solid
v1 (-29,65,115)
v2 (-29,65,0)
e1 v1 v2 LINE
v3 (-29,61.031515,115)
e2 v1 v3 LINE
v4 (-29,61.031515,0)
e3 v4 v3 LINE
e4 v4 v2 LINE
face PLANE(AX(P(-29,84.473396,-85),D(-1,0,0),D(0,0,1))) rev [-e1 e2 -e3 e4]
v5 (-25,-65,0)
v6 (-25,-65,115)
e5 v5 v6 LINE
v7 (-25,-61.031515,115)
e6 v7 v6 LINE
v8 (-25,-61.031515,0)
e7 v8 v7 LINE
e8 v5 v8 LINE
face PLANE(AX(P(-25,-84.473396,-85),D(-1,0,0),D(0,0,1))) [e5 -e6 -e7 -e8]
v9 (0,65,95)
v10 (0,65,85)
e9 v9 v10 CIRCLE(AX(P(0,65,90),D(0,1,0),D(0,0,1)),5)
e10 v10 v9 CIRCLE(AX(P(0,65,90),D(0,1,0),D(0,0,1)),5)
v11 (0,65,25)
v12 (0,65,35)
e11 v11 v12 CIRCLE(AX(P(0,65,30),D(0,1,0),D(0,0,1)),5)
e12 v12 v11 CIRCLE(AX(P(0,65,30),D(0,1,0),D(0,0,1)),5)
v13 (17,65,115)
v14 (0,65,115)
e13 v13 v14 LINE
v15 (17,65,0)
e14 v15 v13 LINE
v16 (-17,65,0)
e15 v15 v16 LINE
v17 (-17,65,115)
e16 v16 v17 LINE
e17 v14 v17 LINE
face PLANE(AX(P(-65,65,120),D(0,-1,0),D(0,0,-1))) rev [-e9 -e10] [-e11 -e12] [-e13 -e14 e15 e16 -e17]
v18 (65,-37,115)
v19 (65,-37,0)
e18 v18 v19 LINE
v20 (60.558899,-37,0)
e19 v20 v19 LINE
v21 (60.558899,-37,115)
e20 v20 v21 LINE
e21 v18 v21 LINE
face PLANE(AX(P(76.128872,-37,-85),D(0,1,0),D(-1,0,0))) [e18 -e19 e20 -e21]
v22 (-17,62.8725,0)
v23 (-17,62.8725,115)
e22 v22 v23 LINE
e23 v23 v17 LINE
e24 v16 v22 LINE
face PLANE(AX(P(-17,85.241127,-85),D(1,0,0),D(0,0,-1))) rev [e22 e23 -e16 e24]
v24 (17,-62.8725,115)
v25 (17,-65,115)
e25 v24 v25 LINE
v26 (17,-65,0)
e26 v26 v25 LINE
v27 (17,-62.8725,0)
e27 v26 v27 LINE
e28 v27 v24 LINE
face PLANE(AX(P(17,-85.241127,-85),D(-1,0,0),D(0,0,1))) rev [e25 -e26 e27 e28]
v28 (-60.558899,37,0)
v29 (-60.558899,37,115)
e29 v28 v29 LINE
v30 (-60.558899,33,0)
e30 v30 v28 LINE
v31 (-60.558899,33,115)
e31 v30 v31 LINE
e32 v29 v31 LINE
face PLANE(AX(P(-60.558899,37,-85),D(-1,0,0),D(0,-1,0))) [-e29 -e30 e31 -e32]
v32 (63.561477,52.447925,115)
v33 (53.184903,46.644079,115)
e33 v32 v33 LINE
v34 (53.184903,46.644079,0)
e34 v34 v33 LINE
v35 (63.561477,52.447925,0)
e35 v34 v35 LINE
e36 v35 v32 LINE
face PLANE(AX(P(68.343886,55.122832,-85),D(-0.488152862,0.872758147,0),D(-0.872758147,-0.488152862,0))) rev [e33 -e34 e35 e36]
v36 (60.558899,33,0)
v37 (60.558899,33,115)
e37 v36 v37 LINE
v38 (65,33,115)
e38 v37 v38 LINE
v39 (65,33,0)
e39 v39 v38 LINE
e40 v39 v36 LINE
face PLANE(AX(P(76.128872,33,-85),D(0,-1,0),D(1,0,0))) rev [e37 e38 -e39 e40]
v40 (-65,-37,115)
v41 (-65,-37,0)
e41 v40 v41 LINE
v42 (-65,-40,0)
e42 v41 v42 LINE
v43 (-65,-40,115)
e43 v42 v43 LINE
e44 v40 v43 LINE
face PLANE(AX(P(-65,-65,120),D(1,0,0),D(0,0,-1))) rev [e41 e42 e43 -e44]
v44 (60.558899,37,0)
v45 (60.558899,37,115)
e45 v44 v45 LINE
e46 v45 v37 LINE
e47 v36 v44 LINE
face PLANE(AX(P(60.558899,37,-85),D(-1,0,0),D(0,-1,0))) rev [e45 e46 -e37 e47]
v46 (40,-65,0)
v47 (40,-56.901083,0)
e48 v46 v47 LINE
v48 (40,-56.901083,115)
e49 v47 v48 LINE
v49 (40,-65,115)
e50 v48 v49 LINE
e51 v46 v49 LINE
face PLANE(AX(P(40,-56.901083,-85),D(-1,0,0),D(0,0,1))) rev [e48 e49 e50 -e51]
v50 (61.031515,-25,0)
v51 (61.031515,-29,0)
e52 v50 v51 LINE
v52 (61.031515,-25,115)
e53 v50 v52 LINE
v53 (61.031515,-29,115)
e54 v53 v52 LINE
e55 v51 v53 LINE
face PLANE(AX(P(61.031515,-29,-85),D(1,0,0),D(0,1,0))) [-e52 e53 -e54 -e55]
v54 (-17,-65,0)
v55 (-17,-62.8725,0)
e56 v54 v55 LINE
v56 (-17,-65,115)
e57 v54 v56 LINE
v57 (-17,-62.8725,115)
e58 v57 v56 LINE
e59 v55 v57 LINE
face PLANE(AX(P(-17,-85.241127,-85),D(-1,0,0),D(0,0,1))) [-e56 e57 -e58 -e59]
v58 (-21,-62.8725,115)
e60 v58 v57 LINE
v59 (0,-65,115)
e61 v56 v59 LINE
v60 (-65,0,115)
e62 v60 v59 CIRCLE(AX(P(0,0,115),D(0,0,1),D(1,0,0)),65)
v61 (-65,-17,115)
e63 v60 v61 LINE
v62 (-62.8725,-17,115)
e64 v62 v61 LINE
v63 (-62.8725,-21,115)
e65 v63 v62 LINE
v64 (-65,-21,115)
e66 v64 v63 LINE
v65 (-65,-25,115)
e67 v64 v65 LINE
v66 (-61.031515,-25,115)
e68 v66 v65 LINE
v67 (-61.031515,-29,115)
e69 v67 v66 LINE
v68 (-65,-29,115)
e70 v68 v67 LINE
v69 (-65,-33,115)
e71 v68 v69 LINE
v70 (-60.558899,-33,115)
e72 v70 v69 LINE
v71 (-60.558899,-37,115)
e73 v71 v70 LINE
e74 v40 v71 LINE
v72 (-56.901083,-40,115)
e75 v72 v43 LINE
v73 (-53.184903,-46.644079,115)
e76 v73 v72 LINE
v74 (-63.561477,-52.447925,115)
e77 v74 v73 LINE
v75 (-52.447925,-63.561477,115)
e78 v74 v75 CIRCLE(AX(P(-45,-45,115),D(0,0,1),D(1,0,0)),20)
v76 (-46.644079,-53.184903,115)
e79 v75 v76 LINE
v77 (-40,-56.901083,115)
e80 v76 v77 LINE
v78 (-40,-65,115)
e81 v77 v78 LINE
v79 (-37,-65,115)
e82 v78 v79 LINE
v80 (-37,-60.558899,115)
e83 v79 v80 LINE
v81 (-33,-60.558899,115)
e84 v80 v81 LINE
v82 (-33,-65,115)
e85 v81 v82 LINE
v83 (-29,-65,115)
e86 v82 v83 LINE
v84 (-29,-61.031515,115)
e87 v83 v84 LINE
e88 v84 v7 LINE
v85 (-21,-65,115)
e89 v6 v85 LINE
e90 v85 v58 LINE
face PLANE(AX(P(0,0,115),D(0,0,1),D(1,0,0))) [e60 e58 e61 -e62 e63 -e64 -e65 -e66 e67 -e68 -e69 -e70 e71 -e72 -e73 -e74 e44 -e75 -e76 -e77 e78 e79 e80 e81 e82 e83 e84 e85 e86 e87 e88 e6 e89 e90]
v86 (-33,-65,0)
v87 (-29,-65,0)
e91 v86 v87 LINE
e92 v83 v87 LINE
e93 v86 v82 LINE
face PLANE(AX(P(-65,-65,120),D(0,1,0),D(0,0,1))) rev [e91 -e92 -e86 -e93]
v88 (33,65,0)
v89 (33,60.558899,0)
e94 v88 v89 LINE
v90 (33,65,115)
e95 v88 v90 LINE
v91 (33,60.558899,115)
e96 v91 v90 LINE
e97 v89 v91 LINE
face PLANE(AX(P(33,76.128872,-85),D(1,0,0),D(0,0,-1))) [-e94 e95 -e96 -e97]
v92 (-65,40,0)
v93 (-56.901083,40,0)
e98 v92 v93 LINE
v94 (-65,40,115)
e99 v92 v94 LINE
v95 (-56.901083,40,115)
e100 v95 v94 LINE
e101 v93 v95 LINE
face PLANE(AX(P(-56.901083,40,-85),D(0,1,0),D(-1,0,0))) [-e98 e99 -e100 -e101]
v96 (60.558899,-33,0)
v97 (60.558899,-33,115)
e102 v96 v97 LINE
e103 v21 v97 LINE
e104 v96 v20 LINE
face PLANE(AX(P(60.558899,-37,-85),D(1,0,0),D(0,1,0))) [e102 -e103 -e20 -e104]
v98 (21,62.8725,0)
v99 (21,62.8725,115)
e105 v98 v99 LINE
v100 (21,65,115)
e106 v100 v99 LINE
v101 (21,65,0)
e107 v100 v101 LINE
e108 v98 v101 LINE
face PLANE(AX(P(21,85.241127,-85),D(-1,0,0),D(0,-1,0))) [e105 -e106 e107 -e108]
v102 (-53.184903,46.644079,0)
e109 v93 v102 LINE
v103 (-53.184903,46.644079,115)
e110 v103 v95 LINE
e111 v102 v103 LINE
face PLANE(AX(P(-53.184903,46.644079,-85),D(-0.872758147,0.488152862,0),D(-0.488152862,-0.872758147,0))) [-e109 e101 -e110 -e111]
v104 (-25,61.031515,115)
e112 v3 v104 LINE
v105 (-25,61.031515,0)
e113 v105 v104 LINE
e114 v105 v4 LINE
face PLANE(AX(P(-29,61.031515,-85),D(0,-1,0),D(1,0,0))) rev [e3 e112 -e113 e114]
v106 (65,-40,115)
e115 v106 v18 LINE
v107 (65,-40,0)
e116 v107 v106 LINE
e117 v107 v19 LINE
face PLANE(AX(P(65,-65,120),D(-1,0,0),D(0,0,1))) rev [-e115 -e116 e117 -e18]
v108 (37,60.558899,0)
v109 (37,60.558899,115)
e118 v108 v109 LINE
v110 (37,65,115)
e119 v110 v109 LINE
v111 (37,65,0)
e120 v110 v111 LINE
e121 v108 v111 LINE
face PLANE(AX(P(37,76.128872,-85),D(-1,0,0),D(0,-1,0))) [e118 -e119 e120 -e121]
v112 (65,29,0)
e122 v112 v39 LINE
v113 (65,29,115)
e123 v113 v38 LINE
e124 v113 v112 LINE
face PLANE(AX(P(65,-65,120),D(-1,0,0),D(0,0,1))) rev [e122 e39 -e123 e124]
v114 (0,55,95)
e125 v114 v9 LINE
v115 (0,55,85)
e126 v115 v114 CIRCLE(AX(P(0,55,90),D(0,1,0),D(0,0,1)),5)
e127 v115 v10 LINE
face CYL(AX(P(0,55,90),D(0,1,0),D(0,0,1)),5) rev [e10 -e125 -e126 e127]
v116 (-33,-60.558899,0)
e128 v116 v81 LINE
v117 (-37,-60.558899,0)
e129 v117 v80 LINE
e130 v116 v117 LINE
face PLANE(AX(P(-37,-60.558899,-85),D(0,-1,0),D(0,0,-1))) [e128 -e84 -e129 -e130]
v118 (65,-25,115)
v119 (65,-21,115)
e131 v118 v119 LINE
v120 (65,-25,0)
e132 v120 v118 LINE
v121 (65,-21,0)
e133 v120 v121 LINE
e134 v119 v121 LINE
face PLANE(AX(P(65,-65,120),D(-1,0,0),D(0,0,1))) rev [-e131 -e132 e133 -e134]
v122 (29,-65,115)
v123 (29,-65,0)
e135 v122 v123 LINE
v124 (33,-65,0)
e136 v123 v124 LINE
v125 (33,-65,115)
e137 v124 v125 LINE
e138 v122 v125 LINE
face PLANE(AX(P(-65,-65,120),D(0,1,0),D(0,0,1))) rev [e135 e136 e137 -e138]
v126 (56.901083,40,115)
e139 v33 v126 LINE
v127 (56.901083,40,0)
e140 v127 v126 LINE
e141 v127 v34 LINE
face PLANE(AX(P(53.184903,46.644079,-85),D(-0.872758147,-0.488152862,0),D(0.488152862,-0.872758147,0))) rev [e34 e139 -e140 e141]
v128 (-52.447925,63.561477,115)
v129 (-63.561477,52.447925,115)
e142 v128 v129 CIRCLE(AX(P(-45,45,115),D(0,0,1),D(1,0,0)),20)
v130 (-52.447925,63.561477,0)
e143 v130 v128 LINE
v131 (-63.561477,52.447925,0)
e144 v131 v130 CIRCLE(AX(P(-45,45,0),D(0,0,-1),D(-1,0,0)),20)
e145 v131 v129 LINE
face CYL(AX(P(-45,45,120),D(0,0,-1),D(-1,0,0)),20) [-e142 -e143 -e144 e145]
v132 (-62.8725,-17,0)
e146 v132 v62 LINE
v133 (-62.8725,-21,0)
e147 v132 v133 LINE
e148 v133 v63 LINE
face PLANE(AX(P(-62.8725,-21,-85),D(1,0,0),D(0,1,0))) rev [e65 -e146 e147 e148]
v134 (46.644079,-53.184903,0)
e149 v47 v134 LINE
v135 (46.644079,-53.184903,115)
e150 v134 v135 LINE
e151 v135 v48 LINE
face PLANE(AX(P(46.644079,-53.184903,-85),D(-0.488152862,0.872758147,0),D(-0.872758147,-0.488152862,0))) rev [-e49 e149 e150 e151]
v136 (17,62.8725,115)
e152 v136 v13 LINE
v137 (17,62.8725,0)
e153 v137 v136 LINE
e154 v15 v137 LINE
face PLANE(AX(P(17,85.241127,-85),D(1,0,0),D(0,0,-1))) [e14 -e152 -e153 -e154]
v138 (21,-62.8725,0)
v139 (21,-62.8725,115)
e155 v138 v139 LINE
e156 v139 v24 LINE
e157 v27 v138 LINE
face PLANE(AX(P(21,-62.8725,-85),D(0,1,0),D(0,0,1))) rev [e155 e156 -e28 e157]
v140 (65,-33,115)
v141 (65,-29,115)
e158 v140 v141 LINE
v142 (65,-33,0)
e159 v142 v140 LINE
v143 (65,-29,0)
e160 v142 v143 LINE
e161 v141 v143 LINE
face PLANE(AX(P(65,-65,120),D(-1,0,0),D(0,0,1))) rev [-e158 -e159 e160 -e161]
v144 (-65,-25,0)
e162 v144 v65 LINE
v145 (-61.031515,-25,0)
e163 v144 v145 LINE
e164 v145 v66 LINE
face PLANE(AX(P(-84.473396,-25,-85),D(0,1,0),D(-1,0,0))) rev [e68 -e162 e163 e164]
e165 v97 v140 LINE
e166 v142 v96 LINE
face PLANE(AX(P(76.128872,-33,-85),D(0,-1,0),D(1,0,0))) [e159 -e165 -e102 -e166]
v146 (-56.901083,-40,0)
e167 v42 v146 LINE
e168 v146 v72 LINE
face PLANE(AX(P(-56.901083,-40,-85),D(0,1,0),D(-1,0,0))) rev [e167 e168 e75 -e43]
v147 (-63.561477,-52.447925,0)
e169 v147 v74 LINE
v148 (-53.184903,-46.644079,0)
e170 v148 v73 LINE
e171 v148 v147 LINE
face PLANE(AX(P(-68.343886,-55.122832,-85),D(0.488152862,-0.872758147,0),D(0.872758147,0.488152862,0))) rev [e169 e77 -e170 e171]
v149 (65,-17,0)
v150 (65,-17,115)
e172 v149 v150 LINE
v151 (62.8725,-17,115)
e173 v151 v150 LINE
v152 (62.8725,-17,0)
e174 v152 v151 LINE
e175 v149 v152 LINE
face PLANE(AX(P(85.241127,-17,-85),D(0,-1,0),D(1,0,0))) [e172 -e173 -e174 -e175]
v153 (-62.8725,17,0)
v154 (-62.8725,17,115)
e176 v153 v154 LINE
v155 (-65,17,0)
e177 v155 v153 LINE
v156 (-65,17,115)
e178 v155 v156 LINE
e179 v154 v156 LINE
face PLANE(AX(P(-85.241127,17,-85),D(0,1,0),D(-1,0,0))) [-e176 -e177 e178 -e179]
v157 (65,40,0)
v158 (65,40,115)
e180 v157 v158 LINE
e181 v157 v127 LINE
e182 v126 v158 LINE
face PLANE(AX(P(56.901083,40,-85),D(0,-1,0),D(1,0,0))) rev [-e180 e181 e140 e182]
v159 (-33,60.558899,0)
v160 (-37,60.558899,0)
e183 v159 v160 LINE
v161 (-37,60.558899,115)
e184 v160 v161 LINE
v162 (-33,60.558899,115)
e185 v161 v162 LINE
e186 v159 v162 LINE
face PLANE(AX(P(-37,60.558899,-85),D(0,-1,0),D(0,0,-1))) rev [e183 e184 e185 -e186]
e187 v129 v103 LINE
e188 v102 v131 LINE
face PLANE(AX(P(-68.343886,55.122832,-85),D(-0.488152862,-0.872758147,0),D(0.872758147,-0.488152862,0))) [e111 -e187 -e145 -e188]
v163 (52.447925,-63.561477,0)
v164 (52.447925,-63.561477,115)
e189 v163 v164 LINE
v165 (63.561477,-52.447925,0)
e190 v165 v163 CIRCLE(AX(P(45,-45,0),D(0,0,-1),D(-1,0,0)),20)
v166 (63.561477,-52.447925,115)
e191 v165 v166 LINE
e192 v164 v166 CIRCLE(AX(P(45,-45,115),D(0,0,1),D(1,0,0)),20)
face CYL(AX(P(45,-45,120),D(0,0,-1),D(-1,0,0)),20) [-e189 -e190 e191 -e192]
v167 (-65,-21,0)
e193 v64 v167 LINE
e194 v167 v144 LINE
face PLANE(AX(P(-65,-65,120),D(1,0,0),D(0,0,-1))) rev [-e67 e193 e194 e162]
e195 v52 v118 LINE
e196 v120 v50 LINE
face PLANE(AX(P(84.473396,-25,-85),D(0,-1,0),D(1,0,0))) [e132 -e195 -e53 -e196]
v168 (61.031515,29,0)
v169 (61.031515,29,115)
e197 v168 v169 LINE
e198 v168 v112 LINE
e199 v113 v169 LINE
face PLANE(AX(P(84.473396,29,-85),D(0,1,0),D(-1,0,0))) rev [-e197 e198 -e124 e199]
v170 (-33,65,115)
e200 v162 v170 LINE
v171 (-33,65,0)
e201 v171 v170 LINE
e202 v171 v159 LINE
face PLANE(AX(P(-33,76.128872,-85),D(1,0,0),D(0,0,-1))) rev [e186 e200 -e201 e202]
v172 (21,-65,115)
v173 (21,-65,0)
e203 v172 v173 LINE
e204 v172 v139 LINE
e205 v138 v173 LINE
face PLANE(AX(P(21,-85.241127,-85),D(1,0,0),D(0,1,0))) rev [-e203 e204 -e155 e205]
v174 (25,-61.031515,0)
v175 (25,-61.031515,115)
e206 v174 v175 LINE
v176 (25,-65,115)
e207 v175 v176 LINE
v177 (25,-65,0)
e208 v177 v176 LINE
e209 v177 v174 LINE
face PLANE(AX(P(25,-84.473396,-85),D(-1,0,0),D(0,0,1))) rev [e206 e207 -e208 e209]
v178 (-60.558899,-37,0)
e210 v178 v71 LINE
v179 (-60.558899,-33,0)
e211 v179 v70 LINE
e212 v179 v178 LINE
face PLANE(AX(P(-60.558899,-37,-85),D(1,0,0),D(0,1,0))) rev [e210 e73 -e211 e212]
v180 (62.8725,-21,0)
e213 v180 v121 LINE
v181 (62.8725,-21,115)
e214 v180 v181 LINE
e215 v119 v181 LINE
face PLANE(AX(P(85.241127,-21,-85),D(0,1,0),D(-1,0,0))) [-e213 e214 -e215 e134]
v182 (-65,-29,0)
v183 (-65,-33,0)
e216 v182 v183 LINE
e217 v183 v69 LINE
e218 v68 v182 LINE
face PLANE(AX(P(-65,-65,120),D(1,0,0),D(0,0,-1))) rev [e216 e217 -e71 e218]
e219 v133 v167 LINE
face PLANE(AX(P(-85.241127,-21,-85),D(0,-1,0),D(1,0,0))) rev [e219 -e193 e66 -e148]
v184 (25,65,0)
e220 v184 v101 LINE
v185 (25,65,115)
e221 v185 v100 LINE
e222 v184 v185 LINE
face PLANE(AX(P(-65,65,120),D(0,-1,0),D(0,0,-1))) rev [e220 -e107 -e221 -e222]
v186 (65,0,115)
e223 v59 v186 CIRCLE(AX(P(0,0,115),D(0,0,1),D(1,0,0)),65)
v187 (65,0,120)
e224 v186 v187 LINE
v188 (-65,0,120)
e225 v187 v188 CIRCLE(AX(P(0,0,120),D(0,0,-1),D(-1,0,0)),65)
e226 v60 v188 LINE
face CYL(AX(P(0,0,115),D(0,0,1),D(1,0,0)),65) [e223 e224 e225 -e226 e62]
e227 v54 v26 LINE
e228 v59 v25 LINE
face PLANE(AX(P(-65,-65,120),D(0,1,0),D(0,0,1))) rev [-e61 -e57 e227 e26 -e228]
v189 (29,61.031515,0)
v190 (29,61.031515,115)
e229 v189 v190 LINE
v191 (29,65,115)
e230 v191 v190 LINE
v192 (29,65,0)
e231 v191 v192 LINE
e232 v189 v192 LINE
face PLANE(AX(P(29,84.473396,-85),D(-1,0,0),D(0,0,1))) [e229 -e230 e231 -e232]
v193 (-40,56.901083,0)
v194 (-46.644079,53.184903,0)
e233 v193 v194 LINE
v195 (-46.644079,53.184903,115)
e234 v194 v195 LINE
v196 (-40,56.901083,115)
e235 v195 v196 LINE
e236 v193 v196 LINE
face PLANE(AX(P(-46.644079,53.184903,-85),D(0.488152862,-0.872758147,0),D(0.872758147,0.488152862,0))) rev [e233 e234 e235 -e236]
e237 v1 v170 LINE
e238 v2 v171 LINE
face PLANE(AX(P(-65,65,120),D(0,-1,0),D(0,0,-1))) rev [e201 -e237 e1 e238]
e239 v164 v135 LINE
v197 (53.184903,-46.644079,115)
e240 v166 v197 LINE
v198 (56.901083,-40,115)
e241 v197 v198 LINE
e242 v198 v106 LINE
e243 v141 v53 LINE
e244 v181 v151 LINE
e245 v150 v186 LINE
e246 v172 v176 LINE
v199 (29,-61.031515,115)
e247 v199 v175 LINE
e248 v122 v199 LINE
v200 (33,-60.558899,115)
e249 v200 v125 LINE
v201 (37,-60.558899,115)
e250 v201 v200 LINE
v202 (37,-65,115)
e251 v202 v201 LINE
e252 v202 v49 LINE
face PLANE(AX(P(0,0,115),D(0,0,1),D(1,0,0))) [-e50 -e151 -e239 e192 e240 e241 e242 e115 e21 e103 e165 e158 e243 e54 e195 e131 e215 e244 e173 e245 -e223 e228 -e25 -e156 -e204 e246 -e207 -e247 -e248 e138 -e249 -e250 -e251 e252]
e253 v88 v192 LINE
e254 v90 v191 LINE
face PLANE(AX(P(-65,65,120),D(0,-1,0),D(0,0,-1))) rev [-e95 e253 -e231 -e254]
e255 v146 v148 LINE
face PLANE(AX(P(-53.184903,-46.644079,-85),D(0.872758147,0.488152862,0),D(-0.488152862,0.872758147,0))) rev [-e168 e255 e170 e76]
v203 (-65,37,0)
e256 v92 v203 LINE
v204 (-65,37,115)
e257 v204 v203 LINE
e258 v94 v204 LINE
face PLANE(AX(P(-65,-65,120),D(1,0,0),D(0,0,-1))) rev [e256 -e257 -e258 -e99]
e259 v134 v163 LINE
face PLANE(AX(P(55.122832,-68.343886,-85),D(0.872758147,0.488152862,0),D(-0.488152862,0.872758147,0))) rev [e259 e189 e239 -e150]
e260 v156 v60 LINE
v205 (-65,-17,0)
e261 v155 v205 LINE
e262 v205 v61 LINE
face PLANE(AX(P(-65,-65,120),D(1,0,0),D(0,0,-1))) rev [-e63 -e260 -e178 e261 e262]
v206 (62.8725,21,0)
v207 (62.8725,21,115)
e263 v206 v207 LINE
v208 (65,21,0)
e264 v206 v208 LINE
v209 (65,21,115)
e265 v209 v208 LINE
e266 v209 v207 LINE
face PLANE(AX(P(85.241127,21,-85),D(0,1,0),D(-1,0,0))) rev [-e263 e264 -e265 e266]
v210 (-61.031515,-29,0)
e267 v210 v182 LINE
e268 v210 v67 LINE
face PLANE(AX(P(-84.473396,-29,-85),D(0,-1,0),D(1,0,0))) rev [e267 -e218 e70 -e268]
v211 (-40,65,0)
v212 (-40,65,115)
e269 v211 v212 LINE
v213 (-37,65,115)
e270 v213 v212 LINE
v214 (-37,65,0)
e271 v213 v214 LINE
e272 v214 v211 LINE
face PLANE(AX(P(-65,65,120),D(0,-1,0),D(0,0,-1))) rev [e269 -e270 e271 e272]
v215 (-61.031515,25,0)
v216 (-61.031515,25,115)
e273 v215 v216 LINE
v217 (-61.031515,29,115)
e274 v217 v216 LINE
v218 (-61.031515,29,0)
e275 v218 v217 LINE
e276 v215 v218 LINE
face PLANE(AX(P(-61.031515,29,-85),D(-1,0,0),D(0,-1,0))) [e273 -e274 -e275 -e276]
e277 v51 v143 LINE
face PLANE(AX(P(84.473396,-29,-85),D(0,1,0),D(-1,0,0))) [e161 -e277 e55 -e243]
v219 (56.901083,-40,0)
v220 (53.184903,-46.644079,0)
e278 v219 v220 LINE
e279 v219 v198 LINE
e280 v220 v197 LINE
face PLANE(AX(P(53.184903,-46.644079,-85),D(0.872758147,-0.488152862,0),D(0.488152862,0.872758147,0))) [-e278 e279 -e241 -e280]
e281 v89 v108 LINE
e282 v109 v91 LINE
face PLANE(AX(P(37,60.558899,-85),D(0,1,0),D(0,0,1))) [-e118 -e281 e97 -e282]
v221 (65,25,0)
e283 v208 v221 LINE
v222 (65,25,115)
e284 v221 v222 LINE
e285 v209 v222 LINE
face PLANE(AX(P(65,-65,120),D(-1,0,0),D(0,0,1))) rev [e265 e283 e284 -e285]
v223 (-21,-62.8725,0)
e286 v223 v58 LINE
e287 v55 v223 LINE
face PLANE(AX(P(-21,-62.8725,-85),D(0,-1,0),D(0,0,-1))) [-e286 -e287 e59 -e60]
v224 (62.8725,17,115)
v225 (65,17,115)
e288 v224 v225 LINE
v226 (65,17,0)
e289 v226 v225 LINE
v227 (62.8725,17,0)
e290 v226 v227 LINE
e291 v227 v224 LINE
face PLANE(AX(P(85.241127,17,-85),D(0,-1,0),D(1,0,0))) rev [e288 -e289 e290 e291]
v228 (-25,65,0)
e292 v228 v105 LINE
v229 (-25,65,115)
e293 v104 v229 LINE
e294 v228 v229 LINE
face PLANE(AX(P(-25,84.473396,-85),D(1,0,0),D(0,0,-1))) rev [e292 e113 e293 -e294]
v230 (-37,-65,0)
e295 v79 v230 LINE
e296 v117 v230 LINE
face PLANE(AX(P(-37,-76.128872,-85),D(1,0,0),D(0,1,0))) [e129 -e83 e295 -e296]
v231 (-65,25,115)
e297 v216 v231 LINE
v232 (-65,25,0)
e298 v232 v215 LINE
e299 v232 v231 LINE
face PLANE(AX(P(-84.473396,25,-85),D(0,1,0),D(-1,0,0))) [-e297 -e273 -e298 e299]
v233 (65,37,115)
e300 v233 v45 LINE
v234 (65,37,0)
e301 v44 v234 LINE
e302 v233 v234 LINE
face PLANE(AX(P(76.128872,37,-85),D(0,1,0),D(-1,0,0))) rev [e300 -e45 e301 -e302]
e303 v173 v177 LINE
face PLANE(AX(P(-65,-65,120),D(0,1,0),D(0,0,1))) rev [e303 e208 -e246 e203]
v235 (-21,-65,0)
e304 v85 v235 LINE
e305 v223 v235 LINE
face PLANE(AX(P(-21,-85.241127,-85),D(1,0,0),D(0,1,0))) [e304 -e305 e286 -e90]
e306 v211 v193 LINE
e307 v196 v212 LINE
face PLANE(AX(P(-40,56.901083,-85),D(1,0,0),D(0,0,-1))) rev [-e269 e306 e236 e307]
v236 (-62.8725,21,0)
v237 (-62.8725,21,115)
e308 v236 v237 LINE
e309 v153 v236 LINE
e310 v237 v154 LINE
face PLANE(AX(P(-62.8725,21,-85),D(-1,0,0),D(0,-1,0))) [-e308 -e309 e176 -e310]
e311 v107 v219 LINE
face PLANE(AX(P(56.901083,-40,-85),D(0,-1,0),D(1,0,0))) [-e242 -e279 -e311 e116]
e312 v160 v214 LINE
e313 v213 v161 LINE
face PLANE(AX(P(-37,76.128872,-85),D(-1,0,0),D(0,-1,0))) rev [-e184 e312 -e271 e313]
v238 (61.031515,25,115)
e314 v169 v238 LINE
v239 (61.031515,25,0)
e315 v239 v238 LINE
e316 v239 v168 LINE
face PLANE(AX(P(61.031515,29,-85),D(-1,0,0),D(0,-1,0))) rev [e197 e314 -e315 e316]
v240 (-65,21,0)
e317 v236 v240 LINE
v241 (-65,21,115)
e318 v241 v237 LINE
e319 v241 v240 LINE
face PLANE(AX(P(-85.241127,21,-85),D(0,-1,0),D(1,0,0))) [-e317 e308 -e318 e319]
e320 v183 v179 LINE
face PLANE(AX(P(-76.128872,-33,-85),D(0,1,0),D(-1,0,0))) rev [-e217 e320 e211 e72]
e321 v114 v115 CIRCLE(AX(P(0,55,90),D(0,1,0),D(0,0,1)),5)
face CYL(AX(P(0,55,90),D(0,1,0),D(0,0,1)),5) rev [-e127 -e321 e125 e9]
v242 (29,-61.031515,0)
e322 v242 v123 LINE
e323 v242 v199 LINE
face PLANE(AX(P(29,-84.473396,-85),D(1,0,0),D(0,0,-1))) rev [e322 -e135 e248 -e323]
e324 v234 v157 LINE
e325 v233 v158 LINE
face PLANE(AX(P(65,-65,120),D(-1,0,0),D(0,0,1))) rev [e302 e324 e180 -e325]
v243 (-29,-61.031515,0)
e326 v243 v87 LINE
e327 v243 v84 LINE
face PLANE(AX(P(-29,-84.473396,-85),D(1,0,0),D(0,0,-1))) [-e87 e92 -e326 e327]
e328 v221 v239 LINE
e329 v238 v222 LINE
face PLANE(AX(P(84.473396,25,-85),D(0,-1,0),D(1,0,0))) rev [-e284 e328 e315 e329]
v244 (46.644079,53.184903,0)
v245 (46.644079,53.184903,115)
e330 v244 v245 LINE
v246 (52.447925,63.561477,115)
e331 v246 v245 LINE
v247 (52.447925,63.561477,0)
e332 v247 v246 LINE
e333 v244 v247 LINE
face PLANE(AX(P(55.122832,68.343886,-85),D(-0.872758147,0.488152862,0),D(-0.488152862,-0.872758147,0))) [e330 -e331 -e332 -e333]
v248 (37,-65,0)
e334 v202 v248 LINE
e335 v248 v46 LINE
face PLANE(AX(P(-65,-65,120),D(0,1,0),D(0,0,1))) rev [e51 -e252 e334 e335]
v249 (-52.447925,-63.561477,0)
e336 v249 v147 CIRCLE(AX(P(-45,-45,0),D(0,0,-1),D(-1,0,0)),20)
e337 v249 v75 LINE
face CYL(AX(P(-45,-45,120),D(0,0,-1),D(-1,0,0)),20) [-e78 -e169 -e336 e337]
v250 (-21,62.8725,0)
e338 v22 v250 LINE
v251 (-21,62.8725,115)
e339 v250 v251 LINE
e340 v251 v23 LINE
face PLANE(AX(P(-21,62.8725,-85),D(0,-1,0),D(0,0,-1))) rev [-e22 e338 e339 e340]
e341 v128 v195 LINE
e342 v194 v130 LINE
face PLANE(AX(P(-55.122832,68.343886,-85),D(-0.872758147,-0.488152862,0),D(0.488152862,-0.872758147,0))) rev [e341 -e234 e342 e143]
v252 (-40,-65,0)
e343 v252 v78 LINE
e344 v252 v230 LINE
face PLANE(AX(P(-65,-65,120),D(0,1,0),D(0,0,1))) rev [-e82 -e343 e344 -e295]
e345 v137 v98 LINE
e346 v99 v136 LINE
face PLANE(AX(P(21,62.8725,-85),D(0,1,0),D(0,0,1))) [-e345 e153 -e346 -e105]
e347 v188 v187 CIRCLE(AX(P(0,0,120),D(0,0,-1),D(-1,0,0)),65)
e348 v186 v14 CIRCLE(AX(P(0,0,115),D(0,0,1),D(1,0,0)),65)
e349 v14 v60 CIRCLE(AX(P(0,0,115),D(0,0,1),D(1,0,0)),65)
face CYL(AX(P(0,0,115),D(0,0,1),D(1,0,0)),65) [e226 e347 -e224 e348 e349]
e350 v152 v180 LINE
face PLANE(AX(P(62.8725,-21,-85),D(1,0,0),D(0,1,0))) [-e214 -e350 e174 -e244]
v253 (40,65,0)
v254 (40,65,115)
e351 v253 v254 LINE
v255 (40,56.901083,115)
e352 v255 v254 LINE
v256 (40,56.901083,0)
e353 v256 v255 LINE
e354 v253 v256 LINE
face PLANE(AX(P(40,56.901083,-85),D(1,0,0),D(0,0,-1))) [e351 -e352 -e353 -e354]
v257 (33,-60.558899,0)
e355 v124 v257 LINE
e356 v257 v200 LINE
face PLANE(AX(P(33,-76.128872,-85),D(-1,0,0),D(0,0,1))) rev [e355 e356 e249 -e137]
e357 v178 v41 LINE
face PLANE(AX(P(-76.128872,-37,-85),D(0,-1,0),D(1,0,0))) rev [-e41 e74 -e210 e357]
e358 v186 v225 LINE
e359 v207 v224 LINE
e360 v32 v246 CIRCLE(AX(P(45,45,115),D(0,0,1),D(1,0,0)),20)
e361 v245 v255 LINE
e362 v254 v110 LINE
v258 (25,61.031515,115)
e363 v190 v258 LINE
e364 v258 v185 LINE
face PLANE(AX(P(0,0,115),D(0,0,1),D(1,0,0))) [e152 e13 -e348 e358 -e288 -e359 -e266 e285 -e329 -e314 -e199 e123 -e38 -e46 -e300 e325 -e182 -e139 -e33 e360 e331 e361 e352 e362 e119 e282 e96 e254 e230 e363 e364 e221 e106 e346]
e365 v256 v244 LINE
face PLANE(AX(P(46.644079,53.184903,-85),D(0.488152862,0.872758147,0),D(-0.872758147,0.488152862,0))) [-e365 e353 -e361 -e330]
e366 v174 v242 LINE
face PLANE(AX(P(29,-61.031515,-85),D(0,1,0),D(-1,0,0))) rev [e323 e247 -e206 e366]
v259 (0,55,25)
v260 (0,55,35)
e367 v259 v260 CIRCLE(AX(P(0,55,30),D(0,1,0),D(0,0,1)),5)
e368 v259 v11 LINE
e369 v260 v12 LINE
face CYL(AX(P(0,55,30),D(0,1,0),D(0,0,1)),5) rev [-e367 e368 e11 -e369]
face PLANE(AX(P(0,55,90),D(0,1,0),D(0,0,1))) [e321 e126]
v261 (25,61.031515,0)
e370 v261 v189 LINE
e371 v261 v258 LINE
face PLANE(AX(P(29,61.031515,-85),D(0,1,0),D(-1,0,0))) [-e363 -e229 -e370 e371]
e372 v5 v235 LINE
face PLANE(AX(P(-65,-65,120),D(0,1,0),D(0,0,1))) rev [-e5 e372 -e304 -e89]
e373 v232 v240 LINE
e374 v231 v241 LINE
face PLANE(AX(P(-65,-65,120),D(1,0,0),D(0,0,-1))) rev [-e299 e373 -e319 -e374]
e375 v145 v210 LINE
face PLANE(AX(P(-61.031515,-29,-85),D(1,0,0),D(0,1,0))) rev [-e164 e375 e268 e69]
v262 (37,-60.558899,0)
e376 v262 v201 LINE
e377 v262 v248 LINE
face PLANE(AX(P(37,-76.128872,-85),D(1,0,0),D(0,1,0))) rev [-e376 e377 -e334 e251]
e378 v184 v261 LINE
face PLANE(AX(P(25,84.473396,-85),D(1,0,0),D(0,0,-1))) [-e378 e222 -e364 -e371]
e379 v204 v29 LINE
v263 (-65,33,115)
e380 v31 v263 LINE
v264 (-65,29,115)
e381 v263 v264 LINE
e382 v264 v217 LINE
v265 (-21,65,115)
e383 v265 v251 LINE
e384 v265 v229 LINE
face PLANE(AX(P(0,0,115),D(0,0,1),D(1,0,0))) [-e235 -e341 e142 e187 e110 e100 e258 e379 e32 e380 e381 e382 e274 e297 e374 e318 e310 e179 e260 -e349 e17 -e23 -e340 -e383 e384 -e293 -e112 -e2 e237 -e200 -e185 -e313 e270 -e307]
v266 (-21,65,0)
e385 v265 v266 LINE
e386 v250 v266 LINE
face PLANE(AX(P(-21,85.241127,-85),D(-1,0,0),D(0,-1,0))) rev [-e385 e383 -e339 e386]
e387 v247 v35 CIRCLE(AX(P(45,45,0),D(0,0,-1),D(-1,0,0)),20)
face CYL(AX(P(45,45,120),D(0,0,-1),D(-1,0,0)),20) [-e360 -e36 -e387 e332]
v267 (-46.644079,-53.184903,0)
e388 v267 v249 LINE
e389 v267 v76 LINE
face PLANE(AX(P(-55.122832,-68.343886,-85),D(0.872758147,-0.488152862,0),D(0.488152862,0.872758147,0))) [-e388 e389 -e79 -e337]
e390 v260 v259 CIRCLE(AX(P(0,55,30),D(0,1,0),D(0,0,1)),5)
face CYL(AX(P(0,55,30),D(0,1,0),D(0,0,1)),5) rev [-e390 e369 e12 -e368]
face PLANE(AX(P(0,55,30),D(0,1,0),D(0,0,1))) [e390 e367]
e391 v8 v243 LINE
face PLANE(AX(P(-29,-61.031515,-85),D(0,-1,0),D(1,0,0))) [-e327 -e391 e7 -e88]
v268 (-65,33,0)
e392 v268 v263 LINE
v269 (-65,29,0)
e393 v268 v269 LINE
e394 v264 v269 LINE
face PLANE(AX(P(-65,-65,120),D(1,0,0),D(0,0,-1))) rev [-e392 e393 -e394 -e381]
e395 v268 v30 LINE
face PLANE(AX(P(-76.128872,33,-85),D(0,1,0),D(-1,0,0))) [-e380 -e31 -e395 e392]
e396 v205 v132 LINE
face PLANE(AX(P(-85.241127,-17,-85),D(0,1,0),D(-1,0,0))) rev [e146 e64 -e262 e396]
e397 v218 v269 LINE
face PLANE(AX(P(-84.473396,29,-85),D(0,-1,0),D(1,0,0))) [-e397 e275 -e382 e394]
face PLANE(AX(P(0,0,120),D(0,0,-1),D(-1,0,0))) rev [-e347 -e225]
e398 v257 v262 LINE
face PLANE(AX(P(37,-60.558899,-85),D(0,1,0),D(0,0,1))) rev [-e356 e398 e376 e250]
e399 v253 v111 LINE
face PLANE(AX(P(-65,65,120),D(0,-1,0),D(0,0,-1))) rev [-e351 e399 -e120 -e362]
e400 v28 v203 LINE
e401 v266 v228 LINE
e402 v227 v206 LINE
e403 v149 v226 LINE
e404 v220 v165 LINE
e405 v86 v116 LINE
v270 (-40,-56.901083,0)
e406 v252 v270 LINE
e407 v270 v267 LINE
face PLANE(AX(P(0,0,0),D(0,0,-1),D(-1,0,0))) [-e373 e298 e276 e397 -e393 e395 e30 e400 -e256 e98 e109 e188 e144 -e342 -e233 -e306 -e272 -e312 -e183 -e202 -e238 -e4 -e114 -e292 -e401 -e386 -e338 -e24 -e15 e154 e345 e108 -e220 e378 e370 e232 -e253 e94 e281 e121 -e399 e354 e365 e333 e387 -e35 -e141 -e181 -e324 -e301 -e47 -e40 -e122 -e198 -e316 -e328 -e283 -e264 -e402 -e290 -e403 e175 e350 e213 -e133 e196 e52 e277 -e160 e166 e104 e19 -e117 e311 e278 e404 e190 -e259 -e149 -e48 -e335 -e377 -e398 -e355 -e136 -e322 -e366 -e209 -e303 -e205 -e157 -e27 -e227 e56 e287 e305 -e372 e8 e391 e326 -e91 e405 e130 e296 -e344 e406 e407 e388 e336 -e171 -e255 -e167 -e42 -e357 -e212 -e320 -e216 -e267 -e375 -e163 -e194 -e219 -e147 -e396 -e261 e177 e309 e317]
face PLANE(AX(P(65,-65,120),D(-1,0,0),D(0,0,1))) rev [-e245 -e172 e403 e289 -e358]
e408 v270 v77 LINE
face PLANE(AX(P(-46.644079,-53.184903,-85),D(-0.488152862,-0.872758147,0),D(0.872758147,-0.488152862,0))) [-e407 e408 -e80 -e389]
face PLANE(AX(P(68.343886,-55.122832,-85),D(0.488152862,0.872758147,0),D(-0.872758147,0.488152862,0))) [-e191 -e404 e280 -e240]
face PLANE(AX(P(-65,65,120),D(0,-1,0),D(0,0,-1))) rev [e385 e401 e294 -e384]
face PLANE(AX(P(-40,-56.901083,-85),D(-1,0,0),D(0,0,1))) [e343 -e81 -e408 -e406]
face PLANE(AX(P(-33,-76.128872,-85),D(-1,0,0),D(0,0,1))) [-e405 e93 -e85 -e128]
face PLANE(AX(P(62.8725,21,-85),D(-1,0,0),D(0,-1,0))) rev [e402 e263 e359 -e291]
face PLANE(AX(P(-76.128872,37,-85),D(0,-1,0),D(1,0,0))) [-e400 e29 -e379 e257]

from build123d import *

# Parameters (mm, degrees)
SKETCH2_W                     = 130
SKETCH2_H                     = 130
BOSS_EXTRUDE2_DEPTH           = 120
SKETCH3_R                     = 110.525507452
SKETCH3_R_2                   = 65
CUT_EXTRUDE1_DEPTH            = 5
FILLET1_R                     = 20
SKETCH4_W                     = 4
SKETCH4_H                     = 15.569973817
SKETCH4_H_2                   = 23.441880492
SKETCH4_H_3                   = 22.368627222
CUT_EXTRUDE2_DEPTH            = 200
CIRPATTERN2_COUNT             = 4
CIRPATTERN2_COPY_1_SKETCH_W   = 4
CIRPATTERN2_COPY_1_SKETCH_H   = 15.569973817
CIRPATTERN2_COPY_1_SKETCH_H_2 = 23.441880492
CIRPATTERN2_COPY_1_SKETCH_H_3 = 22.368627222
CIRPATTERN2_COPY_1_DEPTH      = 200
CIRPATTERN2_COPY_2_SKETCH_W   = 4
CIRPATTERN2_COPY_2_SKETCH_H   = 15.569973817
CIRPATTERN2_COPY_2_SKETCH_H_2 = 23.441880492
CIRPATTERN2_COPY_2_SKETCH_H_3 = 22.368627222
CIRPATTERN2_COPY_2_DEPTH      = 200
CIRPATTERN2_COPY_3_SKETCH_W   = 4
CIRPATTERN2_COPY_3_SKETCH_H   = 15.569973817
CIRPATTERN2_COPY_3_SKETCH_H_2 = 23.441880492
CIRPATTERN2_COPY_3_SKETCH_H_3 = 22.368627222
CIRPATTERN2_COPY_3_DEPTH      = 200
SKETCH5_R                     = 5
CUT_EXTRUDE3_DEPTH            = 10


with BuildPart() as part:
    # Sketch2 → Boss-Extrude2 (new body)
    with BuildSketch(Plane.XY):
        Rectangle(SKETCH2_W, SKETCH2_H)
    extrude(amount=BOSS_EXTRUDE2_DEPTH)

    # Sketch3 → Cut-Extrude1 (cut)
    with BuildSketch(Plane.XY.offset(120)):
        Circle(SKETCH3_R)
        with Locations(Location((0, 0, 0), (0, 0, 180))):
            Circle(SKETCH3_R_2, mode=Mode.SUBTRACT)
    extrude(amount=-CUT_EXTRUDE1_DEPTH, mode=Mode.SUBTRACT)

    # Fillet1
    fillet1_edges = [part.edges().sort_by_distance(p)[0] for p in [
        (65, -65, 57.5),
        (-65, -65, 57.5),
        (-65, 65, 57.5),
        (65, 65, 57.5),
    ]]
    fillet(fillet1_edges, radius=FILLET1_R)

    # Sketch4 → Cut-Extrude2 (cut)
    with BuildSketch(Plane.XY.offset(115)):
        Polygon((-55.12283176, 68.343885556), (-46.644079041, 53.184903421), (-40, 56.901083224), (-40, 68.343885556), align=None)
        with Locations((-35, 68.343885556)):
            Rectangle(SKETCH4_W, SKETCH4_H)
        with Locations((-27, 72.752455261)):
            Rectangle(SKETCH4_W, SKETCH4_H_2)
        with Locations((-19, 74.056813123)):
            Rectangle(SKETCH4_W, SKETCH4_H_3)
    cut_extrude2 = extrude(amount=-CUT_EXTRUDE2_DEPTH, mode=Mode.SUBTRACT)

    # Mirror1: Cut-Extrude2 across plane
    add(cut_extrude2.mirror(Plane(origin=(0, 0, 0), x_dir=(0, 0, 1), z_dir=(1, 0, 0))), mode=Mode.SUBTRACT)

    # CirPattern2: Cut-Extrude2 ×4 about axis
    cirpattern2_axis = Axis((0, 0, 0), (0, 0, 1))
    for i in range(1, CIRPATTERN2_COUNT):
        add(cut_extrude2.rotate(cirpattern2_axis, i * 360 / CIRPATTERN2_COUNT), mode=Mode.SUBTRACT)

    # CirPattern2 copy 1 sketch → CirPattern2 copy 1 (cut)
    with BuildSketch(Plane(origin=(0, 0, 115), x_dir=(0, -1, 0), z_dir=(0, 0, 1))):
        Polygon((-55.12283176, -68.343885556), (-46.644079041, -53.184903421), (-40, -56.901083224), (-40, -68.343885556), align=None)
        with Locations((-35, -68.343885556)):
            Rectangle(CIRPATTERN2_COPY_1_SKETCH_W, CIRPATTERN2_COPY_1_SKETCH_H)
        with Locations((-27, -72.752455261)):
            Rectangle(CIRPATTERN2_COPY_1_SKETCH_W, CIRPATTERN2_COPY_1_SKETCH_H_2)
        with Locations((-19, -74.056813123)):
            Rectangle(CIRPATTERN2_COPY_1_SKETCH_W, CIRPATTERN2_COPY_1_SKETCH_H_3)
    extrude(amount=-CIRPATTERN2_COPY_1_DEPTH, mode=Mode.SUBTRACT)

    # CirPattern2 copy 2 sketch → CirPattern2 copy 2 (cut)
    with BuildSketch(Plane.XY.offset(115)):
        Polygon((-55.12283176, -68.343885556), (-46.644079041, -53.184903421), (-40, -56.901083224), (-40, -68.343885556), align=None)
        with Locations((-35, -68.343885556)):
            Rectangle(CIRPATTERN2_COPY_2_SKETCH_W, CIRPATTERN2_COPY_2_SKETCH_H)
        with Locations((-27, -72.752455261)):
            Rectangle(CIRPATTERN2_COPY_2_SKETCH_W, CIRPATTERN2_COPY_2_SKETCH_H_2)
        with Locations((-19, -74.056813123)):
            Rectangle(CIRPATTERN2_COPY_2_SKETCH_W, CIRPATTERN2_COPY_2_SKETCH_H_3)
    extrude(amount=-CIRPATTERN2_COPY_2_DEPTH, mode=Mode.SUBTRACT)

    # CirPattern2 copy 3 sketch → CirPattern2 copy 3 (cut)
    with BuildSketch(Plane(origin=(0, 0, 115), x_dir=(0, 1, 0), z_dir=(0, 0, 1))):
        Polygon((-55.12283176, -68.343885556), (-46.644079041, -53.184903421), (-40, -56.901083224), (-40, -68.343885556), align=None)
        with Locations((-35, -68.343885556)):
            Rectangle(CIRPATTERN2_COPY_3_SKETCH_W, CIRPATTERN2_COPY_3_SKETCH_H)
        with Locations((-27, -72.752455261)):
            Rectangle(CIRPATTERN2_COPY_3_SKETCH_W, CIRPATTERN2_COPY_3_SKETCH_H_2)
        with Locations((-19, -74.056813123)):
            Rectangle(CIRPATTERN2_COPY_3_SKETCH_W, CIRPATTERN2_COPY_3_SKETCH_H_3)
    extrude(amount=-CIRPATTERN2_COPY_3_DEPTH, mode=Mode.SUBTRACT)

    # Sketch5 → Cut-Extrude3 (cut)
    with BuildSketch(Plane(origin=(0, 65, 0), x_dir=(1, 0, 0), z_dir=(0, 1, 0))):
        with Locations(Location((0, -90, 0), (0, 0, 270))):
            Circle(SKETCH5_R)
        with Locations(Location((0, -30, 0), (0, 0, 270))):
            Circle(SKETCH5_R)
    extrude(amount=-CUT_EXTRUDE3_DEPTH, mode=Mode.SUBTRACT)


solid = part.part
